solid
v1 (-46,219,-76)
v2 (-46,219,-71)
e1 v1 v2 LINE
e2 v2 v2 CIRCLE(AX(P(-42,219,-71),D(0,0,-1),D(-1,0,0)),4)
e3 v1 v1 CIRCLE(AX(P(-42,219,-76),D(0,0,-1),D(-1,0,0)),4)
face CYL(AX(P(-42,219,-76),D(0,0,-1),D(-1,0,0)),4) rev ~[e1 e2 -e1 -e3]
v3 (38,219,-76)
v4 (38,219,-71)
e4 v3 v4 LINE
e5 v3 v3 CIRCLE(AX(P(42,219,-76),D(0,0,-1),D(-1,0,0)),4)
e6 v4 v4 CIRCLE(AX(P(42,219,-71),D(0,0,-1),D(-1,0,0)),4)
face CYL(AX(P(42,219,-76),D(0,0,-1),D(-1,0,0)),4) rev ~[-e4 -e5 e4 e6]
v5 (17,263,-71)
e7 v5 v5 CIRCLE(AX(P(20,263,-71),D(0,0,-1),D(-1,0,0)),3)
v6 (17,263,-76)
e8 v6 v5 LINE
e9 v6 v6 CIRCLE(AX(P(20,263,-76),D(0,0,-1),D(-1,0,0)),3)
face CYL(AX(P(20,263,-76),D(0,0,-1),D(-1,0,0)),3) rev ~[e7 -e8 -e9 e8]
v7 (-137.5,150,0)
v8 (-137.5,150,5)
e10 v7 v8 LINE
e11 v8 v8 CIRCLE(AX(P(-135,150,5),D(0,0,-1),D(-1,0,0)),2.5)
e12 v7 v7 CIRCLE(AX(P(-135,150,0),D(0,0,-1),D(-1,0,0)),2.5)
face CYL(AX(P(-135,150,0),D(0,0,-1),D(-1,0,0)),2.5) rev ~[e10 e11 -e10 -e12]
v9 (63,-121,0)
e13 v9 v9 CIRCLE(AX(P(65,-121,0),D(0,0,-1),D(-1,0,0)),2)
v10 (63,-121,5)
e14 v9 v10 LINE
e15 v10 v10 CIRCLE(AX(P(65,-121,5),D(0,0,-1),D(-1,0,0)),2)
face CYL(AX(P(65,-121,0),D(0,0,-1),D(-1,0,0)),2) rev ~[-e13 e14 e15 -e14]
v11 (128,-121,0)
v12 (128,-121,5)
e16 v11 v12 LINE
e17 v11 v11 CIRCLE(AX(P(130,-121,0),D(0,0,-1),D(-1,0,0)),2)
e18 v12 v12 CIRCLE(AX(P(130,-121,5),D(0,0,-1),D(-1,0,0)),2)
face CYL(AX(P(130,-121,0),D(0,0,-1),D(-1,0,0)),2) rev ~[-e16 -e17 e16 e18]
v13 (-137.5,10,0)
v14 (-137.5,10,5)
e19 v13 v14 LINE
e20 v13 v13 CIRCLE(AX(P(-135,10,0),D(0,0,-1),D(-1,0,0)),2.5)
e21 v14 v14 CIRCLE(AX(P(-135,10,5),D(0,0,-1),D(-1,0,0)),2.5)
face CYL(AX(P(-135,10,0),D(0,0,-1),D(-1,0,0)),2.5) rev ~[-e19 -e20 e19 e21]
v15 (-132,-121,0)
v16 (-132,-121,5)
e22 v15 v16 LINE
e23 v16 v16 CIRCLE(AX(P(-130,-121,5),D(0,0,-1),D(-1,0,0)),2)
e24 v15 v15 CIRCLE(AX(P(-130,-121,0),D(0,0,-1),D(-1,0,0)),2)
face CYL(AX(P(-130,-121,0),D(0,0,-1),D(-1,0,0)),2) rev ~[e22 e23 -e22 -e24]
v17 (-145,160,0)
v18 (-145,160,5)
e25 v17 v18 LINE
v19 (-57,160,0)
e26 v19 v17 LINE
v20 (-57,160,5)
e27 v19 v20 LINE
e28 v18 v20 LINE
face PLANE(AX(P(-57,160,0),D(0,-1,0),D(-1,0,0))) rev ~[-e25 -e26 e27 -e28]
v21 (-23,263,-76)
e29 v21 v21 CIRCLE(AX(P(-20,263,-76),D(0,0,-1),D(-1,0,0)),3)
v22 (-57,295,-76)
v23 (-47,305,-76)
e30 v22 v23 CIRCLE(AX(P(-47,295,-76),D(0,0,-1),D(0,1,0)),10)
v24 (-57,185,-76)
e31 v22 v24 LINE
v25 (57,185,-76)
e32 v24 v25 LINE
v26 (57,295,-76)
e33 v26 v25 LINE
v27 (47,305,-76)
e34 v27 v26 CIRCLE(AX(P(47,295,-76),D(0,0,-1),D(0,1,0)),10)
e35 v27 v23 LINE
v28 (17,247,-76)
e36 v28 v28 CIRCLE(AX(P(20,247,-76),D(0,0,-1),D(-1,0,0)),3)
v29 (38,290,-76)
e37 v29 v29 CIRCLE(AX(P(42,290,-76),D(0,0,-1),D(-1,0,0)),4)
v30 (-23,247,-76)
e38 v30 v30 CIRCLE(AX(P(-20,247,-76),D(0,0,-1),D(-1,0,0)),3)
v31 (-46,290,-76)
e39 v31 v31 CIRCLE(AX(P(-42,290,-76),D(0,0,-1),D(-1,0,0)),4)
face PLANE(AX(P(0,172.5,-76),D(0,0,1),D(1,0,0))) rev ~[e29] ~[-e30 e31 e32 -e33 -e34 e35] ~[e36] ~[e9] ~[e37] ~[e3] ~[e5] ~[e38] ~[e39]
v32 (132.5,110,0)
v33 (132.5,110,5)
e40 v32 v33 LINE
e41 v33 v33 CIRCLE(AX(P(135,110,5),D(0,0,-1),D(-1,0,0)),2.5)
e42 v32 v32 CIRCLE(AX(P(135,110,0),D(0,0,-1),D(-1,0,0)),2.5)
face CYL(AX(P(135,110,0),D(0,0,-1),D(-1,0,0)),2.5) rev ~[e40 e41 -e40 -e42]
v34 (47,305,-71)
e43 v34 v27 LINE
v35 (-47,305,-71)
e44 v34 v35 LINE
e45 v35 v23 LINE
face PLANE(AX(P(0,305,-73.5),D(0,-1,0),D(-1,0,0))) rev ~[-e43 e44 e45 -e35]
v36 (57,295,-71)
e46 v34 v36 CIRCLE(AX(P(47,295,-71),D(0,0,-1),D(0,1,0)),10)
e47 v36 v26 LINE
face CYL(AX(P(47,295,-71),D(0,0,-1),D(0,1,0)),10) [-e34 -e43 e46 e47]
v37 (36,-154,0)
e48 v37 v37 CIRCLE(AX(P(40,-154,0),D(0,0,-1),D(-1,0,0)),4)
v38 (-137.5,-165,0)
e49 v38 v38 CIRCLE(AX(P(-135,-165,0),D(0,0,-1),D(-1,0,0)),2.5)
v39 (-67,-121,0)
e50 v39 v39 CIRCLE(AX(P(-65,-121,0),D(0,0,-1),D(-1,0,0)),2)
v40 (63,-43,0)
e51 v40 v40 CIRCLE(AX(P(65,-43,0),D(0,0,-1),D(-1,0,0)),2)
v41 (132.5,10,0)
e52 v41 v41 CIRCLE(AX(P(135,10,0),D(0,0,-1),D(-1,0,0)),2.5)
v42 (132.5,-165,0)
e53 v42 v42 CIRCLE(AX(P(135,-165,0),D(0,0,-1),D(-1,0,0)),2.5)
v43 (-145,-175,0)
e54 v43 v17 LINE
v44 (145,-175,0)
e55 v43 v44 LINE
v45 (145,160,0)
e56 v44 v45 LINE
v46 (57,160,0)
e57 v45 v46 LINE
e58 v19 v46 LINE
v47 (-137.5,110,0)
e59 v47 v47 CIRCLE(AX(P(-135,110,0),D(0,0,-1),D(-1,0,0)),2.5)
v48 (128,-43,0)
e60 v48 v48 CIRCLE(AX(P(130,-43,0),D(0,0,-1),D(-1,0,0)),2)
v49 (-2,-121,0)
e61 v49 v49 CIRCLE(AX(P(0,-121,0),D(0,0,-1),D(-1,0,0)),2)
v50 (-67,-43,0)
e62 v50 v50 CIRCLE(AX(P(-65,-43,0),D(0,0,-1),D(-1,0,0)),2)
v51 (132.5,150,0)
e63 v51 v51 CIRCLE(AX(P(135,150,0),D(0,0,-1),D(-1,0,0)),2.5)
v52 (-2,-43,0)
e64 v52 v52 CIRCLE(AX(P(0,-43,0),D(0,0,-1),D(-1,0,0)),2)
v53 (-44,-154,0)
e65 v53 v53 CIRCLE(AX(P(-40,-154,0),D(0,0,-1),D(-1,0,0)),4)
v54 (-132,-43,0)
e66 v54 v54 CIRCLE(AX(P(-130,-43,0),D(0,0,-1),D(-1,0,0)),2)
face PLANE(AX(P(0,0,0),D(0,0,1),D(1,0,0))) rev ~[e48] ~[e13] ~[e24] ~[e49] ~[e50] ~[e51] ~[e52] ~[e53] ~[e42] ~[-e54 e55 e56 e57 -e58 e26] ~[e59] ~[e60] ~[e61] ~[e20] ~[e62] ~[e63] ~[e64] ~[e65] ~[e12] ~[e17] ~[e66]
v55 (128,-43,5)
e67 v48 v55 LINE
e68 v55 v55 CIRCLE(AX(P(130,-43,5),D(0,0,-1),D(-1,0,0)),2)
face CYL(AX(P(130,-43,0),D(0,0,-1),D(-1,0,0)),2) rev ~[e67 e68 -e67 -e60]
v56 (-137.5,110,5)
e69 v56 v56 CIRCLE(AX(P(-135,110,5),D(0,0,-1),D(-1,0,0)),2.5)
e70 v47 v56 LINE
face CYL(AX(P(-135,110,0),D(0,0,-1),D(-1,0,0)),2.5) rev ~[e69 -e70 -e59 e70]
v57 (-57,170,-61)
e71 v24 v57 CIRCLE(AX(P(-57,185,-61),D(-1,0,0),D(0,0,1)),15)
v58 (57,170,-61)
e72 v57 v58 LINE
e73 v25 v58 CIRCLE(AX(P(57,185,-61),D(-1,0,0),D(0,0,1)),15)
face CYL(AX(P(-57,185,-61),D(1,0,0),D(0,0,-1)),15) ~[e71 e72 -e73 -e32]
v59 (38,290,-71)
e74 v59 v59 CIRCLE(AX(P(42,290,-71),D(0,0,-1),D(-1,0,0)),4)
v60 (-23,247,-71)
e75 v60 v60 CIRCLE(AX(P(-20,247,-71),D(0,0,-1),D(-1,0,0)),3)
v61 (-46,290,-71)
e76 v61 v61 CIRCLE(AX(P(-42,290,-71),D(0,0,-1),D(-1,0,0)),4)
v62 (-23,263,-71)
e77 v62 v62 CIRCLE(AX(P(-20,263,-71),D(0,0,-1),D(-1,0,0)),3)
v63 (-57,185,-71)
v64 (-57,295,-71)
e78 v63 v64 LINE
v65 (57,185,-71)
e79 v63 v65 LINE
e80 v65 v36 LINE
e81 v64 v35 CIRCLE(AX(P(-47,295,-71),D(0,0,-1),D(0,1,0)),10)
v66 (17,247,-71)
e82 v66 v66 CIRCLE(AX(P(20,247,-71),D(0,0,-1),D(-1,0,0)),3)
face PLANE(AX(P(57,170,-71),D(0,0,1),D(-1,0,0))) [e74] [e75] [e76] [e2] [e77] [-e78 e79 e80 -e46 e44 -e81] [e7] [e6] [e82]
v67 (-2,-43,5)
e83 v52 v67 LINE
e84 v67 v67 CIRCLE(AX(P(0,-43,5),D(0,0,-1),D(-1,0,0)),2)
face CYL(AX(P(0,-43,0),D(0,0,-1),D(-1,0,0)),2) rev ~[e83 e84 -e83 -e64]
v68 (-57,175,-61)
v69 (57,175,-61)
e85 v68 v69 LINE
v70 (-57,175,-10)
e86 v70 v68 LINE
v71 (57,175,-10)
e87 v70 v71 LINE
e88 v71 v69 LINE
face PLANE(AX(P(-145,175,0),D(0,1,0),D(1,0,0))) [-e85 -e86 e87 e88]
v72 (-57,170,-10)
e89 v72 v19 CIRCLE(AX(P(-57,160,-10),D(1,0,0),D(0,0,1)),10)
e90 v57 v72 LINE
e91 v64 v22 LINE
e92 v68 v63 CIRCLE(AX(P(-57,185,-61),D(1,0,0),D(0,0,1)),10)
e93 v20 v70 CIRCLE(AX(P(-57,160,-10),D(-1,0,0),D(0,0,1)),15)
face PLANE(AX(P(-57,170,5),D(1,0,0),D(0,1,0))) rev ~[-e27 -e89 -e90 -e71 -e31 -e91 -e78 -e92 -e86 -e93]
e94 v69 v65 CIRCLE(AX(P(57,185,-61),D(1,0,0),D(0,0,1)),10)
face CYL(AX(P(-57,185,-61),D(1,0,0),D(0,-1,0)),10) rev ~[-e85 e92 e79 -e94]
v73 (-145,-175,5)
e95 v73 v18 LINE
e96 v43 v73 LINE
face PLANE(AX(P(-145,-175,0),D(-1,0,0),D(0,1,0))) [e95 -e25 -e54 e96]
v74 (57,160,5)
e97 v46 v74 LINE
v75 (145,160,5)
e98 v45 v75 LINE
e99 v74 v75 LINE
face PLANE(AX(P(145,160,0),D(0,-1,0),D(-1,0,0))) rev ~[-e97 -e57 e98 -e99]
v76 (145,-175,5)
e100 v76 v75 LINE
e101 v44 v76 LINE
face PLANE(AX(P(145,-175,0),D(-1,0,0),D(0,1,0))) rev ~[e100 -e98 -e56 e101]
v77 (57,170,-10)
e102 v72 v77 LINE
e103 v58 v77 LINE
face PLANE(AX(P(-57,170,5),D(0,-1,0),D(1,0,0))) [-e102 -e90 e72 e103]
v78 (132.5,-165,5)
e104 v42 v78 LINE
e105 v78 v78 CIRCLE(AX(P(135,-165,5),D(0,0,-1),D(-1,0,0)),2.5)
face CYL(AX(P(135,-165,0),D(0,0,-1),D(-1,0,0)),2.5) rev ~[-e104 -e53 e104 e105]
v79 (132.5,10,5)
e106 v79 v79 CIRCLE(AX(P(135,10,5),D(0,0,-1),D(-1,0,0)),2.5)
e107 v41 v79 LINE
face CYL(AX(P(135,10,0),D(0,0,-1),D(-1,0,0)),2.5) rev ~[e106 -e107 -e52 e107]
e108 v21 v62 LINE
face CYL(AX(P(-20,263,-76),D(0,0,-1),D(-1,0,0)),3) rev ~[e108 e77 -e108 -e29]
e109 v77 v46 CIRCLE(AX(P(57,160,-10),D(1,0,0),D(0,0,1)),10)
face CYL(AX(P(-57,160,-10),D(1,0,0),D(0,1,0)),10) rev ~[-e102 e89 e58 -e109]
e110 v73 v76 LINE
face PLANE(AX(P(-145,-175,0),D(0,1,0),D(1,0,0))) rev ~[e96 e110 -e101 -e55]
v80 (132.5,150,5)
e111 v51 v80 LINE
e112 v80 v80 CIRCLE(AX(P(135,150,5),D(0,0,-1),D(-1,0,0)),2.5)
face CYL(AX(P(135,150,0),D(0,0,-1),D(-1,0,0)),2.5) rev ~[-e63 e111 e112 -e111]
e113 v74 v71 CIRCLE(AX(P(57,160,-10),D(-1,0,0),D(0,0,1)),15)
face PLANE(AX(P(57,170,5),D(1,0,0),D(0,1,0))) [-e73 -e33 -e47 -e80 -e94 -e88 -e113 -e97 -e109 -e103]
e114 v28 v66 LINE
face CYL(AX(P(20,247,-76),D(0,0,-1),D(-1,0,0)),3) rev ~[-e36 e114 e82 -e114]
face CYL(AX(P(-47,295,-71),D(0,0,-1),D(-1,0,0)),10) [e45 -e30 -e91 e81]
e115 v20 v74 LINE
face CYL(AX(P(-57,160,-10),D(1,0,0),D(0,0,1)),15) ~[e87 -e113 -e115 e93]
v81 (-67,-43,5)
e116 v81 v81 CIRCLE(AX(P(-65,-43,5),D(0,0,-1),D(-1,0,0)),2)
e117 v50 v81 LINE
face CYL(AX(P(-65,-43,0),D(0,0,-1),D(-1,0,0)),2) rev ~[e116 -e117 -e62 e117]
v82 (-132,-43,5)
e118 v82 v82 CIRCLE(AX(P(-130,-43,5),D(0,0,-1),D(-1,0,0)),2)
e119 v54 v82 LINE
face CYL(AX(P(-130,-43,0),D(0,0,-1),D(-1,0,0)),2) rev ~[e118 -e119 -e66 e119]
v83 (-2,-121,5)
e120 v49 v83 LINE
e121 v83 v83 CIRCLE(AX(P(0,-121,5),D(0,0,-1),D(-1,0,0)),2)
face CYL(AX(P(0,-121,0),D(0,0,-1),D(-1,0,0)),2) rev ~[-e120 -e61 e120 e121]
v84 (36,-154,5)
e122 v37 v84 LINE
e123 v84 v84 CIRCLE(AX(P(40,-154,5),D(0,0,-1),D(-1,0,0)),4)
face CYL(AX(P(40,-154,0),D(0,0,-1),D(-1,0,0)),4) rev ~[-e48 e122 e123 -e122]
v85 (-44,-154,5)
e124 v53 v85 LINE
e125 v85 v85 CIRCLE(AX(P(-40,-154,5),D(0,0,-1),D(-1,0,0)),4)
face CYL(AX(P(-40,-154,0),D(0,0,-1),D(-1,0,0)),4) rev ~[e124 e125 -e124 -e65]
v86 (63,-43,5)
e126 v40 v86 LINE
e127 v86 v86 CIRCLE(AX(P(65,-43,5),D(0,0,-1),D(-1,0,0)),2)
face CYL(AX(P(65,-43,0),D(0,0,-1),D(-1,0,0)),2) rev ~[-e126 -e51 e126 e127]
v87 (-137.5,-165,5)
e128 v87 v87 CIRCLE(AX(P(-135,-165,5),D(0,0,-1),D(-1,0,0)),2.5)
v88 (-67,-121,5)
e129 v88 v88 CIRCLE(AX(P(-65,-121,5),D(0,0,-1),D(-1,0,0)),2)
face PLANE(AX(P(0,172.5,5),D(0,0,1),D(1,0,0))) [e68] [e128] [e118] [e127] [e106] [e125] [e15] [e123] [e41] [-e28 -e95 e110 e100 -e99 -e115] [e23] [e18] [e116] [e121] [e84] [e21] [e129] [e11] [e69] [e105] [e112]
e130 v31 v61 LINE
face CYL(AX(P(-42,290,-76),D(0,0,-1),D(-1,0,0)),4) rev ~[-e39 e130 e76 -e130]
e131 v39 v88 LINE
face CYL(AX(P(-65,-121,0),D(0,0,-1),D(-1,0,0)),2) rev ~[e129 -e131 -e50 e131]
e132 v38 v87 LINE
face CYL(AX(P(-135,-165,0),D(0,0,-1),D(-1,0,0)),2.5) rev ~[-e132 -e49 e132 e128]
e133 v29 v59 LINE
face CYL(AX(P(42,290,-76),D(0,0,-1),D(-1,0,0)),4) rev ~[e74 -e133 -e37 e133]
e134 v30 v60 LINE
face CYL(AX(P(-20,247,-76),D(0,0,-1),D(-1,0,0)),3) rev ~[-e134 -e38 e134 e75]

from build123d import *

# Parameters (mm, degrees)
SKETCH1_W           = 290
SKETCH1_H           = 350
BOSS_EXTRUDE1_DEPTH = 5
SKETCH2_W           = 114
SKETCH2_H           = 5
BOSS_EXTRUDE2_DEPTH = 81
SKETCH3_W           = 114
SKETCH3_H           = 5
BOSS_EXTRUDE3_DEPTH = 135
FILLET1_R           = 10
SKETCH4_W           = 88
SKETCH4_H           = 15
CUT_EXTRUDE1_DEPTH  = 120
FILLET2_R           = 15
FILLET3_R           = 10
SKETCH5_R           = 4
CUT_EXTRUDE2_DEPTH  = 120
SKETCH7_R           = 2
CUT_EXTRUDE3_DEPTH  = 10
SKETCH8_R           = 3
CUT_EXTRUDE4_DEPTH  = 10
SKETCH9_R           = 4
CUT_EXTRUDE5_DEPTH  = 10
SKETCH10_R          = 2.5
CUT_EXTRUDE6_DEPTH  = 10
SKETCH11_R          = 2.5
CUT_EXTRUDE7_DEPTH  = 10


with BuildPart() as part:
    # Sketch1 → Boss-Extrude1 (new body)
    with BuildSketch(Plane.XY):
        Rectangle(SKETCH1_W, SKETCH1_H)
    extrude(amount=BOSS_EXTRUDE1_DEPTH)

    # Sketch2 → Boss-Extrude2 (add)
    with BuildSketch(Plane.XY.offset(5)):
        with Locations((0, 172.5)):
            Rectangle(SKETCH2_W, SKETCH2_H)
    extrude(amount=-BOSS_EXTRUDE2_DEPTH)

    # Sketch3 → Boss-Extrude3 (add)
    with BuildSketch(Plane(origin=(0, 170, 0), x_dir=(-1, 0, 0), z_dir=(0, -1, 0))):
        with Locations((0, 73.5)):
            Rectangle(SKETCH3_W, SKETCH3_H)
    extrude(amount=-BOSS_EXTRUDE3_DEPTH)

    # Fillet1
    fillet1_edges = [part.edges().sort_by_distance(p)[0] for p in [
        (0, 170, 0),
        (0, 175, -71),
    ]]
    fillet(fillet1_edges, radius=FILLET1_R)

    # Sketch4 → Cut-Extrude1 (cut)
    with BuildSketch(Plane(origin=(0, 0, 0), x_dir=(-1, 0, 0), z_dir=(0, 0, -1))):
        with Locations((101, 167.5)):
            Rectangle(SKETCH4_W, SKETCH4_H)
        with Locations((-101, 167.5)):
            Rectangle(SKETCH4_W, SKETCH4_H)
    extrude(amount=-CUT_EXTRUDE1_DEPTH, mode=Mode.SUBTRACT)

    # Fillet2
    fillet2_edges = [part.edges().sort_by_distance(p)[0] for p in [
        (0, 175, 5),
        (0, 170, -76),
    ]]
    fillet(fillet2_edges, radius=FILLET2_R)

    # Fillet3
    fillet3_edges = [part.edges().sort_by_distance(p)[0] for p in [
        (57, 305, -73.5),
        (-57, 305, -73.5),
    ]]
    fillet(fillet3_edges, radius=FILLET3_R)

    # Sketch5 → Cut-Extrude2 (cut)
    with BuildSketch(Plane(origin=(0, 0, -76), x_dir=(-1, 0, 0), z_dir=(0, 0, -1))):
        with Locations((42, 290)):
            Circle(SKETCH5_R)
        with Locations((-42, 290)):
            Circle(SKETCH5_R)
        with Locations((42, 219)):
            Circle(SKETCH5_R)
        with Locations((-42, 219)):
            Circle(SKETCH5_R)
    extrude(amount=-CUT_EXTRUDE2_DEPTH, mode=Mode.SUBTRACT)

    # Sketch7 → Cut-Extrude3 (cut)
    with BuildSketch(Plane(origin=(0, 0, 0), x_dir=(-1, 0, 0), z_dir=(0, 0, -1))):
        with Locations((-130, -121)):
            Circle(SKETCH7_R)
        with Locations((-65, -121)):
            Circle(SKETCH7_R)
        with Locations((0, -121)):
            Circle(SKETCH7_R)
        with Locations((65, -121)):
            Circle(SKETCH7_R)
        with Locations((130, -121)):
            Circle(SKETCH7_R)
        with Locations((130, -43)):
            Circle(SKETCH7_R)
        with Locations((65, -43)):
            Circle(SKETCH7_R)
        with Locations((0, -43)):
            Circle(SKETCH7_R)
        with Locations((-65, -43)):
            Circle(SKETCH7_R)
        with Locations((-130, -43)):
            Circle(SKETCH7_R)
    extrude(amount=-CUT_EXTRUDE3_DEPTH, mode=Mode.SUBTRACT)

    # Sketch8 → Cut-Extrude4 (cut)
    with BuildSketch(Plane(origin=(0, 0, -76), x_dir=(-1, 0, 0), z_dir=(0, 0, -1))):
        with Locations((-20, 247)):
            Circle(SKETCH8_R)
        with Locations((-20, 263)):
            Circle(SKETCH8_R)
        with Locations((20, 263)):
            Circle(SKETCH8_R)
        with Locations((20, 247)):
            Circle(SKETCH8_R)
    extrude(amount=-CUT_EXTRUDE4_DEPTH, mode=Mode.SUBTRACT)

    # Sketch9 → Cut-Extrude5 (cut)
    with BuildSketch(Plane(origin=(0, 0, 0), x_dir=(-1, 0, 0), z_dir=(0, 0, -1))):
        with Locations((40, -154)):
            Circle(SKETCH9_R)
        with Locations((-40, -154)):
            Circle(SKETCH9_R)
    extrude(amount=-CUT_EXTRUDE5_DEPTH, mode=Mode.SUBTRACT)

    # Sketch10 → Cut-Extrude6 (cut)
    with BuildSketch(Plane(origin=(0, 0, 0), x_dir=(-1, 0, 0), z_dir=(0, 0, -1))):
        with Locations((-135, -165)):
            Circle(SKETCH10_R)
        with Locations((135, -165)):
            Circle(SKETCH10_R)
        with Locations((135, 150)):
            Circle(SKETCH10_R)
        with Locations((-135, 150)):
            Circle(SKETCH10_R)
    extrude(amount=-CUT_EXTRUDE6_DEPTH, mode=Mode.SUBTRACT)

    # Sketch11 → Cut-Extrude7 (cut)
    with BuildSketch(Plane(origin=(0, 0, 0), x_dir=(-1, 0, 0), z_dir=(0, 0, -1))):
        with Locations((135, 110)):
            Circle(SKETCH11_R)
        with Locations((135, 10)):
            Circle(SKETCH11_R)
        with Locations((-135, 110)):
            Circle(SKETCH11_R)
        with Locations((-135, 10)):
            Circle(SKETCH11_R)
    extrude(amount=-CUT_EXTRUDE7_DEPTH, mode=Mode.SUBTRACT)


solid = part.part
